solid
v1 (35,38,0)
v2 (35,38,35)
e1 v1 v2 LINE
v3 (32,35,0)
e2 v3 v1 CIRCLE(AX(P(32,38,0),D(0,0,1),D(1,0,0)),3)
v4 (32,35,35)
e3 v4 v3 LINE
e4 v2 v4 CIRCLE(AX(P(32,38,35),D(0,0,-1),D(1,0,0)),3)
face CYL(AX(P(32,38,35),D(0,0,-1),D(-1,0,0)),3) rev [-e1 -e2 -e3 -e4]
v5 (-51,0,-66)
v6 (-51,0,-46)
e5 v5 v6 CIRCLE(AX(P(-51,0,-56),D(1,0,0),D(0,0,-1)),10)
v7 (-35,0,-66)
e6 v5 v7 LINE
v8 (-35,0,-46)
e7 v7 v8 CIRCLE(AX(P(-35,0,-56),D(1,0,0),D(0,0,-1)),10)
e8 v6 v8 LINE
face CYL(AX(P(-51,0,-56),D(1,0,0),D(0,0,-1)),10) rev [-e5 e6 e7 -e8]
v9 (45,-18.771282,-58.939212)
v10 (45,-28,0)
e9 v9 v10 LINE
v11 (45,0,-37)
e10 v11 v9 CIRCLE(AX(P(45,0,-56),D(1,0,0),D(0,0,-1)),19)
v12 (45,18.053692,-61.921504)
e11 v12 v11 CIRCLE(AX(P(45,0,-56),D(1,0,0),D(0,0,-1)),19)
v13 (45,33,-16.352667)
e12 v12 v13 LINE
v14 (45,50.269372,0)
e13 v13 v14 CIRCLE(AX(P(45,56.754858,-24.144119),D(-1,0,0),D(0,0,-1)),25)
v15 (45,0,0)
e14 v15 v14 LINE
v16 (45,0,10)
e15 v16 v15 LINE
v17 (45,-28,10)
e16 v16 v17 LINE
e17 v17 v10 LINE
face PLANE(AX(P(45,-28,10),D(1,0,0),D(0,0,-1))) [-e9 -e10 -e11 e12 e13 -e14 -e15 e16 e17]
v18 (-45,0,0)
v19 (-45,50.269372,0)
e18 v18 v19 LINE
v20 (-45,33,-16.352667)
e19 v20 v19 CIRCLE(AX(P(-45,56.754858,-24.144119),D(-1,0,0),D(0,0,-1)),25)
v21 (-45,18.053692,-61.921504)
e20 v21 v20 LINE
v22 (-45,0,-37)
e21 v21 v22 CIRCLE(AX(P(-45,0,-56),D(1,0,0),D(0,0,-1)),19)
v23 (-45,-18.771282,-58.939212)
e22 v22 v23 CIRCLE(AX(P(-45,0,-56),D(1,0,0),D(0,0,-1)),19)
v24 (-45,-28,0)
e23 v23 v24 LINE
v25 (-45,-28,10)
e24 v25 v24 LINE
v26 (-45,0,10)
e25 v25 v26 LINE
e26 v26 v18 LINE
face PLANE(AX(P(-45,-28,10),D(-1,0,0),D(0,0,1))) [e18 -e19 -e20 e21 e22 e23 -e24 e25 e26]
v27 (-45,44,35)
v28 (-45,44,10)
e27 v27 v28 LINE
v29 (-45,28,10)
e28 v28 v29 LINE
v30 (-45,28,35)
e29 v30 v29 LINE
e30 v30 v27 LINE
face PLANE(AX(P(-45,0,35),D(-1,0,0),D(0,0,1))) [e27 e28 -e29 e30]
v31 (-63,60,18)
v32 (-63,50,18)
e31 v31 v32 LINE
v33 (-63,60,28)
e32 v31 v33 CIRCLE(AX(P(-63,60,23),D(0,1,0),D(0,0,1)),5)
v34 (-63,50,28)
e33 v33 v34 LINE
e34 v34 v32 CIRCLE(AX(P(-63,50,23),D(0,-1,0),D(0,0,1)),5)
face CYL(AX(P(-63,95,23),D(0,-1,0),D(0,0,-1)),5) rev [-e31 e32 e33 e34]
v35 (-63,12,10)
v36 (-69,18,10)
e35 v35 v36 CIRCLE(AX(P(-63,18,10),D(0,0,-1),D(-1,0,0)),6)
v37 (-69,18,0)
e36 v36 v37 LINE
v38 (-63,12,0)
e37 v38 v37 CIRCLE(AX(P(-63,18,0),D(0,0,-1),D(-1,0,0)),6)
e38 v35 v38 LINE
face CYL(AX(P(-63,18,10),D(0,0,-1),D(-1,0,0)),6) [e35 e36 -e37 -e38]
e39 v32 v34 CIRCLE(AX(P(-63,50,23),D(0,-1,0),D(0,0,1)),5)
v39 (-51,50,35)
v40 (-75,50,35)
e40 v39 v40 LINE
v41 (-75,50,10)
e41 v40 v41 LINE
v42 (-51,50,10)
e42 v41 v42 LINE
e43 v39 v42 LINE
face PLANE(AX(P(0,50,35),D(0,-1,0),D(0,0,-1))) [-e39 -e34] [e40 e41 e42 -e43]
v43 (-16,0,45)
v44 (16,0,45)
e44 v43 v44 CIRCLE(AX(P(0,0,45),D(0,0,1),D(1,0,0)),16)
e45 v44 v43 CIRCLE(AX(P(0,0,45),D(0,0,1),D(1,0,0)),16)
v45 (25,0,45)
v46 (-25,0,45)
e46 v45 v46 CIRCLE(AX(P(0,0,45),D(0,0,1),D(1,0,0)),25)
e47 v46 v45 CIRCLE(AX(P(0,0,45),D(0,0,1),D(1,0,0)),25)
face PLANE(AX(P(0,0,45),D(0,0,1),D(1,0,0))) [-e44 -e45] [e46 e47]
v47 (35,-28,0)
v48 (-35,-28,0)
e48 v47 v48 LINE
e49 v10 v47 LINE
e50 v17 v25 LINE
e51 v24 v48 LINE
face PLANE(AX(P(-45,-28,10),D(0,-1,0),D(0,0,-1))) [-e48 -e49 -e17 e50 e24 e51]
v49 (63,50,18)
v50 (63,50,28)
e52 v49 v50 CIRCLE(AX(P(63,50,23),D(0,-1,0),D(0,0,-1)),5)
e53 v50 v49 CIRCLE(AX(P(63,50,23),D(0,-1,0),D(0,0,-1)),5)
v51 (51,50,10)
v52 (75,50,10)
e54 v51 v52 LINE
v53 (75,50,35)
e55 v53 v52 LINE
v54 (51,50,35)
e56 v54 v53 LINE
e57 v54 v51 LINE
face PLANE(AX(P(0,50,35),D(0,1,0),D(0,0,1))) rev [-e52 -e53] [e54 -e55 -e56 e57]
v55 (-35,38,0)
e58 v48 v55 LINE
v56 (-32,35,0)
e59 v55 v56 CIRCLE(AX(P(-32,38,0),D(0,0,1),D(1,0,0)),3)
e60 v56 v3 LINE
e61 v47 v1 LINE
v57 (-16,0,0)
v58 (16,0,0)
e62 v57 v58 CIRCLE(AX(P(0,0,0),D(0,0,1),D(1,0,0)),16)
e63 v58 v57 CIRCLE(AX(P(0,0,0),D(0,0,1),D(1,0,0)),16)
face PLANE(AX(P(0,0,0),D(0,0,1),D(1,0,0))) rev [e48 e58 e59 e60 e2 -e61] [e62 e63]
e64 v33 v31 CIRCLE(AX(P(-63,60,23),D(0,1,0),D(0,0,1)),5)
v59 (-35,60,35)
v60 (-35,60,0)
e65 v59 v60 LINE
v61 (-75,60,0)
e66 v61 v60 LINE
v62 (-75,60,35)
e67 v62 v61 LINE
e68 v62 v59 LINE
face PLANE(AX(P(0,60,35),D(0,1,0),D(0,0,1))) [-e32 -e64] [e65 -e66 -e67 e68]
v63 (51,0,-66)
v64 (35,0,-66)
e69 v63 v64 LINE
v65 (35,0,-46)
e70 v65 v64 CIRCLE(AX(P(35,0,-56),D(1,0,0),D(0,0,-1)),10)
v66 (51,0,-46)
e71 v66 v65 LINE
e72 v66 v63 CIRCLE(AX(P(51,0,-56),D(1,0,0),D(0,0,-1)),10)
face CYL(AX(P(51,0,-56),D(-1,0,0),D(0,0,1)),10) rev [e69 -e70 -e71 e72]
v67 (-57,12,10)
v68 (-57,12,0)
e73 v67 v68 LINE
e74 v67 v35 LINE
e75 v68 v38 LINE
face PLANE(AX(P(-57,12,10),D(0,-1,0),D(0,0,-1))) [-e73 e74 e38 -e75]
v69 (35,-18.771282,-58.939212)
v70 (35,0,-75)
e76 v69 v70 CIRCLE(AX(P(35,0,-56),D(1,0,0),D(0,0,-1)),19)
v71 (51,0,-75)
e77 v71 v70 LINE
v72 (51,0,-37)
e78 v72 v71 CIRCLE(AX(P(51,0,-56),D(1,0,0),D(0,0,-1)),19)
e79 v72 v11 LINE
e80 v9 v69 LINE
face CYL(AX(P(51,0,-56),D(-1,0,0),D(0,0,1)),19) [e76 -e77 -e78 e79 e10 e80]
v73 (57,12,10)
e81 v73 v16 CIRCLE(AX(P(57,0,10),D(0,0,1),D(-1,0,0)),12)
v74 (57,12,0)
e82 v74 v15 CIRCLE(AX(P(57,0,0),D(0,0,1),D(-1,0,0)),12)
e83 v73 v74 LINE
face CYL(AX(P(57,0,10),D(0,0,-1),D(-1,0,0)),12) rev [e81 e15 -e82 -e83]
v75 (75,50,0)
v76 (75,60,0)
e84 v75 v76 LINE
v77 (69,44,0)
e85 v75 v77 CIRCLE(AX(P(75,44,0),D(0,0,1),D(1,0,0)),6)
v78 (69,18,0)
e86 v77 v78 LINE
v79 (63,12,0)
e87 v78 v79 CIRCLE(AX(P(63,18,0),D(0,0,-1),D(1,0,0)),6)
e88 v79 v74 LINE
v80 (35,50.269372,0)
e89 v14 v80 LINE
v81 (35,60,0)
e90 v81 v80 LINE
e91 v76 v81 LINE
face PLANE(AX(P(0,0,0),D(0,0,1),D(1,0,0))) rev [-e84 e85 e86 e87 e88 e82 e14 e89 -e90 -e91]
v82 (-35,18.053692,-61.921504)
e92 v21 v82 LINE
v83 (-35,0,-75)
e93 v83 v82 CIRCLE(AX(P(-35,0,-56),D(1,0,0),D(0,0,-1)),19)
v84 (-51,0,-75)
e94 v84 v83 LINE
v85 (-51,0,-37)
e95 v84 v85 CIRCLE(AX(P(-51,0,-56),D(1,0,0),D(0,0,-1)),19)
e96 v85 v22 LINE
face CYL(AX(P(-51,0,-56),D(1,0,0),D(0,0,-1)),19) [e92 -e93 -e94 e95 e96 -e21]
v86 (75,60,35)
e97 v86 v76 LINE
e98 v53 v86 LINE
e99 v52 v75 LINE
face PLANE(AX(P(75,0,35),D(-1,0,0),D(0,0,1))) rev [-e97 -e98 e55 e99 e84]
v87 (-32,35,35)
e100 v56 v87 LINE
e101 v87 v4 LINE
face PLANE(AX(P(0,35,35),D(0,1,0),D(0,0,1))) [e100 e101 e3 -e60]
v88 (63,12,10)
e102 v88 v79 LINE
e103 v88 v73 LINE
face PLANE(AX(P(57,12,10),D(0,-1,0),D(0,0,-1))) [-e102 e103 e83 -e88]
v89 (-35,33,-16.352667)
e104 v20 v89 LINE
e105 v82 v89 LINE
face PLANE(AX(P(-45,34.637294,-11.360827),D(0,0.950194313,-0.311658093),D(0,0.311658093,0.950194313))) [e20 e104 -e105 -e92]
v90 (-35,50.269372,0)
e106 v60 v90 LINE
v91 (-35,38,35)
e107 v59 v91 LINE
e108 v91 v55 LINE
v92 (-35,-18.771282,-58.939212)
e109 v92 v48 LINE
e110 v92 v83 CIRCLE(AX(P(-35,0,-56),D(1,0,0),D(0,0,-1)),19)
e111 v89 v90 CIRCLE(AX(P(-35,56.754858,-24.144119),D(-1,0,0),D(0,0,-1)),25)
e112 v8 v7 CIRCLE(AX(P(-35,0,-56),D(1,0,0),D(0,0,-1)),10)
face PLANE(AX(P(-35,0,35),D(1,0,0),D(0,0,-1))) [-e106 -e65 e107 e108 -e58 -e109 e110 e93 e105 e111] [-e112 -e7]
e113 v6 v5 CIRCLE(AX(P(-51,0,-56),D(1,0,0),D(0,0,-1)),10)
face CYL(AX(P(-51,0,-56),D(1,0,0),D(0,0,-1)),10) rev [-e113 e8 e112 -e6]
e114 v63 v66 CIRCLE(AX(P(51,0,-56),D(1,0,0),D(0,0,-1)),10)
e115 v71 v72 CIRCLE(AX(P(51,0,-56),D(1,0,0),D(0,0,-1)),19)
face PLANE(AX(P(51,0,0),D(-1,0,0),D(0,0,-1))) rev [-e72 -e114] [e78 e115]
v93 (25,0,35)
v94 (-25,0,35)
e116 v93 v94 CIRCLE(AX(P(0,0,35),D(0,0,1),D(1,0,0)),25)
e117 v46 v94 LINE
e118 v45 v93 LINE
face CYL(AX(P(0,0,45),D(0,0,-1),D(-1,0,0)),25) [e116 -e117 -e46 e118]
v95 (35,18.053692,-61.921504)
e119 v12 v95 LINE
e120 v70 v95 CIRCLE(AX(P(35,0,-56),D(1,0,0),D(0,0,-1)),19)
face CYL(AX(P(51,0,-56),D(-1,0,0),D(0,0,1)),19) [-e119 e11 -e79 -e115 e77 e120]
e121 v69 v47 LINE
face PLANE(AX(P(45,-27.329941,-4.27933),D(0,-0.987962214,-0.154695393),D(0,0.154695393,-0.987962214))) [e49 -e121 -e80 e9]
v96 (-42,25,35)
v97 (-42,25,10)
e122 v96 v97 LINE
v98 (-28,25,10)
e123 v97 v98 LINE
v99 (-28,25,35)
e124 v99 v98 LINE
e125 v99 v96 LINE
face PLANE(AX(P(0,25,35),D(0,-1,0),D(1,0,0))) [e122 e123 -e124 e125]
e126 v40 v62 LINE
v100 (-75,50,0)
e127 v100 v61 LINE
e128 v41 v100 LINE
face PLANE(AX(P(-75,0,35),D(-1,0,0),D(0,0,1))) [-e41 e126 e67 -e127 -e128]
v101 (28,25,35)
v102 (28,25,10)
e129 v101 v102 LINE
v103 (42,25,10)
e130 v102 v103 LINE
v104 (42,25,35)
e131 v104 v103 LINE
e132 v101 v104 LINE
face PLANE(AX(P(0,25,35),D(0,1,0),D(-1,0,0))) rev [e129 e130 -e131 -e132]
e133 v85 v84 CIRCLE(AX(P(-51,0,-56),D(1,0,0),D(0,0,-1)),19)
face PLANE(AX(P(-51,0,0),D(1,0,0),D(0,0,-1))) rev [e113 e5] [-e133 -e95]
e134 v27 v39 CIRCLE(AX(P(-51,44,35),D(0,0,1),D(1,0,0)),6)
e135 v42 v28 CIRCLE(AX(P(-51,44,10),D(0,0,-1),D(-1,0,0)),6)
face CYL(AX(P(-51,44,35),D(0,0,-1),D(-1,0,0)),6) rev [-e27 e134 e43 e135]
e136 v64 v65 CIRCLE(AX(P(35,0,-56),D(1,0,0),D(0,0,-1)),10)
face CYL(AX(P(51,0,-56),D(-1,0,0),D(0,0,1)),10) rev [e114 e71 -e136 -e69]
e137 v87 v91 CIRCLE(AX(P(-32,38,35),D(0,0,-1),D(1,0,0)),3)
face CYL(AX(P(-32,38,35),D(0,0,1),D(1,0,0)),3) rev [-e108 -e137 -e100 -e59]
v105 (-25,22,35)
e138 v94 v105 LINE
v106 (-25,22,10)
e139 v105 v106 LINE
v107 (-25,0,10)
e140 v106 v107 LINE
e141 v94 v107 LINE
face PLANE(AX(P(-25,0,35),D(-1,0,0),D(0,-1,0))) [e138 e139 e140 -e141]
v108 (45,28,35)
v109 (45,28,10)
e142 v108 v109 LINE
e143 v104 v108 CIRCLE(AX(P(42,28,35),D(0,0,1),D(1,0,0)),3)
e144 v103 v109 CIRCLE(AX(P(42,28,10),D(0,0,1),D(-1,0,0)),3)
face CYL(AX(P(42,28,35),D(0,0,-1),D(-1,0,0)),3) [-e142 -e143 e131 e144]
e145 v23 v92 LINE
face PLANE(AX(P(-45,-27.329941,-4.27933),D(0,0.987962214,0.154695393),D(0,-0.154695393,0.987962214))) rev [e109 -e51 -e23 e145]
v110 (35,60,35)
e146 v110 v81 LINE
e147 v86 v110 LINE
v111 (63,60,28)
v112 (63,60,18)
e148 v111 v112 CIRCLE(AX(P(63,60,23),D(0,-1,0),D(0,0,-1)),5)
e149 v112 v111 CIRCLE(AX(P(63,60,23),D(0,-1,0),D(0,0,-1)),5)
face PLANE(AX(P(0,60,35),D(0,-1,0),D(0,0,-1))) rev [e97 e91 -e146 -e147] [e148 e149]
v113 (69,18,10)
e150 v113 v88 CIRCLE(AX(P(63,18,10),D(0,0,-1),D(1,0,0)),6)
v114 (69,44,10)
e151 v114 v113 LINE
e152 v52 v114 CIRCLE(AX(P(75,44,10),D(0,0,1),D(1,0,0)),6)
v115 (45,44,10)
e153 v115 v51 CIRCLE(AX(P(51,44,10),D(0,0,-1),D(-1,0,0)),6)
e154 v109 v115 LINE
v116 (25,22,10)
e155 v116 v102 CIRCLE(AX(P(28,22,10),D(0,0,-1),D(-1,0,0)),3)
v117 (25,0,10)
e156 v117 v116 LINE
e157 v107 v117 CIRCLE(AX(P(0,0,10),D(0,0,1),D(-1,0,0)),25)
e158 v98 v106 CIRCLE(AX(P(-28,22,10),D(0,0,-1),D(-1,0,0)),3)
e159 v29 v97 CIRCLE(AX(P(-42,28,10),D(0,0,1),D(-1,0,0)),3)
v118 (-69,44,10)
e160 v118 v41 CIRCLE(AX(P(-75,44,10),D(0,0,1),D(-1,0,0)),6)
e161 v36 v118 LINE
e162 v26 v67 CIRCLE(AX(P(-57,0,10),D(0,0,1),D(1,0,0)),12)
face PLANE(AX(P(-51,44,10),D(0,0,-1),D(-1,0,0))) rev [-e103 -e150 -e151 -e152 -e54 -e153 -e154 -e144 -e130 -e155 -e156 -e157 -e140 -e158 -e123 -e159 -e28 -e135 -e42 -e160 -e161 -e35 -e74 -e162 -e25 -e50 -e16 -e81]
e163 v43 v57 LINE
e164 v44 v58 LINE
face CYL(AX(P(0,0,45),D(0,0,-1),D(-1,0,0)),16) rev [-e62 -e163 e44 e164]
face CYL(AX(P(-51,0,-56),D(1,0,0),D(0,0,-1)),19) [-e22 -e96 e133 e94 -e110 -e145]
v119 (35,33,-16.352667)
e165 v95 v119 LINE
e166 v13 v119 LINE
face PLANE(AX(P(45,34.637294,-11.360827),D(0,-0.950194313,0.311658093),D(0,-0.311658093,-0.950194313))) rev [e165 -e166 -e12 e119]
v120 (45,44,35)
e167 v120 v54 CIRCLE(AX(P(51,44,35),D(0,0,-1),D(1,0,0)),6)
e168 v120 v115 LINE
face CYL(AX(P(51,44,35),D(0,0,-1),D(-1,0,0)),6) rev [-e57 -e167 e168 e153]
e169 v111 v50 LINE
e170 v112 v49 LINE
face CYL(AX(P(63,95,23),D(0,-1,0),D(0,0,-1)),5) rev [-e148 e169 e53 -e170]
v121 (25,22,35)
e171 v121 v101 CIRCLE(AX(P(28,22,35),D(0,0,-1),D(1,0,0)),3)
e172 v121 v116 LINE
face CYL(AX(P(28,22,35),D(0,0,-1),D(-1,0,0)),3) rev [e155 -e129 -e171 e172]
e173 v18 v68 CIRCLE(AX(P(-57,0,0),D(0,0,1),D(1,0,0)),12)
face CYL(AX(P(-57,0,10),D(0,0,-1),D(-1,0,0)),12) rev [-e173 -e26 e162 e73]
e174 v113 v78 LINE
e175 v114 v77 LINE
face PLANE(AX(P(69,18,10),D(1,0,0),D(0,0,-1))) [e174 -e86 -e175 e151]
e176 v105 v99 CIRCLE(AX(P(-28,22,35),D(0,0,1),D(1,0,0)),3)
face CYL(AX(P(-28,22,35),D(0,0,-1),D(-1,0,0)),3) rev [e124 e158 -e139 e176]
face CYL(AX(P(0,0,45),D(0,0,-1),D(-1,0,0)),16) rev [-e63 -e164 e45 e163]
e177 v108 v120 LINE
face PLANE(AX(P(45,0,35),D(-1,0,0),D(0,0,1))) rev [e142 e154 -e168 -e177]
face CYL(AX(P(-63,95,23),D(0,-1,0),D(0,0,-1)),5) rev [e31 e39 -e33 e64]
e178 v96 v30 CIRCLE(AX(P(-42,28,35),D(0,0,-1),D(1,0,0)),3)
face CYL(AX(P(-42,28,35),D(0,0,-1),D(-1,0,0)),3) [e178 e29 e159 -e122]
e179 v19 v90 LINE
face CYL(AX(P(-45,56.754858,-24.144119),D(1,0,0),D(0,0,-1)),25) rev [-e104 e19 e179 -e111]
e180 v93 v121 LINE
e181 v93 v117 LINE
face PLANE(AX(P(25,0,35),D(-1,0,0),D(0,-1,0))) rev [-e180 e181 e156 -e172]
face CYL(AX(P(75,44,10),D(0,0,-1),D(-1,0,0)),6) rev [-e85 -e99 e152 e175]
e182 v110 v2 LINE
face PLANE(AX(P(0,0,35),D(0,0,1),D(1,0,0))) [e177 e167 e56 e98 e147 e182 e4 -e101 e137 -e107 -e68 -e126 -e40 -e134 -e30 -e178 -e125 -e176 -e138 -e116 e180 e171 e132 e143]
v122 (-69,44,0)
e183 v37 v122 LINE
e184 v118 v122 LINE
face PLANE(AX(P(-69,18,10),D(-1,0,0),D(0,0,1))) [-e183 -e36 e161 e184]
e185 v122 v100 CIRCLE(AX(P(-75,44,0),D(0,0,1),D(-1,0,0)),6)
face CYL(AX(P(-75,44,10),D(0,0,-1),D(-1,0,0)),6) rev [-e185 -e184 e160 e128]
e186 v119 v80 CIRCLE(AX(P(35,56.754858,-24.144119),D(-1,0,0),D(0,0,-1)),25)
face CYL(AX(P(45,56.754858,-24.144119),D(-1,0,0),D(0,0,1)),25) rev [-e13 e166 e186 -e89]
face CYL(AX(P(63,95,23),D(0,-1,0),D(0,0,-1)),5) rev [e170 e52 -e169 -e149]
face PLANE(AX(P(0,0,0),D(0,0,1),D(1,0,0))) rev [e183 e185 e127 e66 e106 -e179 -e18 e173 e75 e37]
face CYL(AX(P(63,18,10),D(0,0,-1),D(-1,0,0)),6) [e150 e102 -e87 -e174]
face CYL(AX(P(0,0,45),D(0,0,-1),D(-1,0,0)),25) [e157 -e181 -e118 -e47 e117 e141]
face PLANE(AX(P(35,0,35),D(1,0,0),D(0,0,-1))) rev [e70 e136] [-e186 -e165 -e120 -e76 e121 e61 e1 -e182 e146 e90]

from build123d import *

# Parameters (mm, degrees)
BRACKET_BODY_35MM_DEPTH           = 35
PROFILE_REGION_EXTRUDE_45MM_DEPTH = 45
SLOT_CUT_SKETCH_R                 = 5
SLOT_CUT_DEPTH                    = 45
MOUNTING_PAD_10MM_DEPTH           = 10
EDGE_FILLET_R3_R                  = 3
SIDE_LUG_ARM_10MM_DEPTH           = 10
SKETCH6_3_R                       = 19
SKETCH6_3_R_2                     = 10
SIDE_LUG_BOSS_16MM_DEPTH          = 16


with BuildPart() as part:
    # Bracket Profile Sketch → Bracket Body 35mm (new body)
    with BuildSketch(Plane.XY):
        with BuildLine():
            Line((0, 35), (0, 25))
            ThreePointArc((0, 25), (17.67766953, 17.67766953), (25, 0))
            Line((25, 0), (25, 22))
            ThreePointArc((25, 22), (25.878679656, 24.121320344), (28, 25))
            Line((28, 25), (42, 25))
            ThreePointArc((42, 25), (44.121320344, 25.878679656), (45, 28))
            Line((45, 28), (45, 44))
            ThreePointArc((45, 44), (46.757359313, 48.242640687), (51, 50))
            Line((51, 50), (75, 50))
            Line((75, 50), (75, 60))
            Line((75, 60), (35, 60))
            Line((35, 60), (35, 35))
            Line((35, 35), (0, 35))
        make_face()
        with BuildLine():
            Line((-25, 22), (-25, 0))
            ThreePointArc((-25, 0), (-17.67766953, 17.67766953), (0, 25))
            Line((0, 25), (0, 35))
            Line((0, 35), (-35, 35))
            Line((-35, 35), (-35, 60))
            Line((-35, 60), (-75, 60))
            Line((-75, 60), (-75, 50))
            Line((-75, 50), (-51, 50))
            ThreePointArc((-51, 50), (-46.757359313, 48.242640687), (-45, 44))
            Line((-45, 44), (-45, 28))
            ThreePointArc((-45, 28), (-44.121320344, 25.878679656), (-42, 25))
            Line((-42, 25), (-28, 25))
            ThreePointArc((-28, 25), (-25.878679656, 24.121320344), (-25, 22))
        make_face()
    extrude(amount=BRACKET_BODY_35MM_DEPTH)

    # Sketch1_3 → Profile Region Extrude 45mm (add)
    with BuildSketch(Plane.XY):
        with BuildLine():
            ThreePointArc((0, 25), (-17.67766953, 17.67766953), (-25, 0))
            ThreePointArc((-25, 0), (-17.67766953, -17.67766953), (0, -25))
            Line((0, -25), (0, -16))
            ThreePointArc((0, -16), (-16, 0), (0, 16))
            Line((0, 16), (0, 25))
        make_face()
        with BuildLine():
            ThreePointArc((25, 0), (17.67766953, 17.67766953), (0, 25))
            Line((0, 25), (0, 16))
            ThreePointArc((0, 16), (11.313708499, 11.313708499), (16, 0))
            ThreePointArc((16, 0), (11.313708499, -11.313708499), (0, -16))
            Line((0, -16), (0, -25))
            ThreePointArc((0, -25), (17.67766953, -17.67766953), (25, 0))
        make_face()
        with BuildLine():
            ThreePointArc((0, 25), (-17.67766953, 17.67766953), (-25, 0))
            ThreePointArc((-25, 0), (-17.67766953, -17.67766953), (0, -25))
            Line((0, -25), (0, -16))
            ThreePointArc((0, -16), (-16, 0), (0, 16))
            Line((0, 16), (0, 25))
        make_face()
        with BuildLine():
            ThreePointArc((25, 0), (17.67766953, 17.67766953), (0, 25))
            Line((0, 25), (0, 16))
            ThreePointArc((0, 16), (11.313708499, 11.313708499), (16, 0))
            ThreePointArc((16, 0), (11.313708499, -11.313708499), (0, -16))
            Line((0, -16), (0, -25))
            ThreePointArc((0, -25), (17.67766953, -17.67766953), (25, 0))
        make_face()
    extrude(amount=PROFILE_REGION_EXTRUDE_45MM_DEPTH)

    # Slot Cut Sketch → Slot Cut (cut)
    with BuildSketch(Plane.XZ.offset(-50)):
        with Locations(Location((63, 23, 0), (0, 0, 270))):
            Circle(SLOT_CUT_SKETCH_R)
        with Locations(Location((-63, 23, 0), (0, 0, 270))):
            Circle(SLOT_CUT_SKETCH_R)
    extrude(amount=-SLOT_CUT_DEPTH, mode=Mode.SUBTRACT)

    # Mounting Pad Sketch → Mounting Pad 10mm (add)
    with BuildSketch(Plane(origin=(0, 0, 0), x_dir=(-1, 0, 0), z_dir=(0, 0, -1))):
        with BuildLine():
            Line((51, 50), (75, 50))
            ThreePointArc((75, 50), (70.757359313, 48.242640687), (69, 44))
            Line((69, 44), (69, 18))
            ThreePointArc((69, 18), (67.242640687, 13.757359313), (63, 12))
            Line((63, 12), (57, 12))
            ThreePointArc((57, 12), (48.514718626, 8.485281374), (45, 0))
            Line((45, 0), (45, -28))
            Line((45, -28), (-45, -28))
            Line((-45, -28), (-45, 0))
            ThreePointArc((-45, 0), (-48.514718626, 8.485281374), (-57, 12))
            Line((-57, 12), (-63, 12))
            ThreePointArc((-63, 12), (-67.242640687, 13.757359313), (-69, 18))
            Line((-69, 18), (-69, 44))
            ThreePointArc((-69, 44), (-70.757359313, 48.242640687), (-75, 50))
            Line((-75, 50), (-51, 50))
            ThreePointArc((-51, 50), (-46.757359313, 48.242640687), (-45, 44))
            Line((-45, 44), (-45, 28))
            ThreePointArc((-45, 28), (-44.121320344, 25.878679656), (-42, 25))
            Line((-42, 25), (-28, 25))
            ThreePointArc((-28, 25), (-25.878679656, 24.121320344), (-25, 22))
            Line((-25, 22), (-25, 0))
            ThreePointArc((-25, 0), (0, -25), (25, 0))
            Line((25, 0), (25, 22))
            ThreePointArc((25, 22), (25.878679656, 24.121320344), (28, 25))
            Line((28, 25), (42, 25))
            ThreePointArc((42, 25), (44.121320344, 25.878679656), (45, 28))
            Line((45, 28), (45, 44))
            ThreePointArc((45, 44), (46.757359313, 48.242640687), (51, 50))
        make_face()
    extrude(amount=-MOUNTING_PAD_10MM_DEPTH)

    # Edge Fillet R3
    edge_fillet_r3_edges = [part.edges().sort_by_distance(p)[0] for p in [
        (35, 35, 17.5),
        (-35, 35, 17.5),
    ]]
    fillet(edge_fillet_r3_edges, radius=EDGE_FILLET_R3_R)

    # Side Lug Sketch → Side Lug Arm 10mm (add)
    with BuildSketch(Plane(origin=(-35, 0, 0), x_dir=(0, 0, -1), z_dir=(1, 0, 0))):
        with BuildLine():
            ThreePointArc((58.939212458, -18.771282059), (37.062002462, 1.533704422), (61.921503767, 18.053691953))
            Line((61.921503767, 18.053691953), (16.35266654, 33))
            ThreePointArc((16.35266654, 33), (5.991213295, 39.565558274), (0, 50.269372176))
            Line((0, 50.269372176), (0, 38))
            Line((0, 38), (0, -28))
            Line((0, -28), (58.939212458, -18.771282059))
        make_face()
    side_lug_arm_10mm = extrude(amount=-SIDE_LUG_ARM_10MM_DEPTH)

    # Sketch6_3 → Side Lug Boss 16mm (add)
    with BuildSketch(Plane(origin=(-35, 0, 0), x_dir=(0, 0, -1), z_dir=(1, 0, 0))):
        with Locations((56, 0)):
            Circle(SKETCH6_3_R)
        with Locations((56, 0)):
            Circle(SKETCH6_3_R_2, mode=Mode.SUBTRACT)
    side_lug_boss_16mm = extrude(amount=-SIDE_LUG_BOSS_16MM_DEPTH)

    # Side Lug Mirror: Side Lug Arm 10mm, Side Lug Boss 16mm across plane
    add(side_lug_arm_10mm.mirror(Plane(origin=(0, 0, 0), x_dir=(0, 0, 1), z_dir=(1, 0, 0))))
    add(side_lug_boss_16mm.mirror(Plane(origin=(0, 0, 0), x_dir=(0, 0, 1), z_dir=(1, 0, 0))))


solid = part.part
